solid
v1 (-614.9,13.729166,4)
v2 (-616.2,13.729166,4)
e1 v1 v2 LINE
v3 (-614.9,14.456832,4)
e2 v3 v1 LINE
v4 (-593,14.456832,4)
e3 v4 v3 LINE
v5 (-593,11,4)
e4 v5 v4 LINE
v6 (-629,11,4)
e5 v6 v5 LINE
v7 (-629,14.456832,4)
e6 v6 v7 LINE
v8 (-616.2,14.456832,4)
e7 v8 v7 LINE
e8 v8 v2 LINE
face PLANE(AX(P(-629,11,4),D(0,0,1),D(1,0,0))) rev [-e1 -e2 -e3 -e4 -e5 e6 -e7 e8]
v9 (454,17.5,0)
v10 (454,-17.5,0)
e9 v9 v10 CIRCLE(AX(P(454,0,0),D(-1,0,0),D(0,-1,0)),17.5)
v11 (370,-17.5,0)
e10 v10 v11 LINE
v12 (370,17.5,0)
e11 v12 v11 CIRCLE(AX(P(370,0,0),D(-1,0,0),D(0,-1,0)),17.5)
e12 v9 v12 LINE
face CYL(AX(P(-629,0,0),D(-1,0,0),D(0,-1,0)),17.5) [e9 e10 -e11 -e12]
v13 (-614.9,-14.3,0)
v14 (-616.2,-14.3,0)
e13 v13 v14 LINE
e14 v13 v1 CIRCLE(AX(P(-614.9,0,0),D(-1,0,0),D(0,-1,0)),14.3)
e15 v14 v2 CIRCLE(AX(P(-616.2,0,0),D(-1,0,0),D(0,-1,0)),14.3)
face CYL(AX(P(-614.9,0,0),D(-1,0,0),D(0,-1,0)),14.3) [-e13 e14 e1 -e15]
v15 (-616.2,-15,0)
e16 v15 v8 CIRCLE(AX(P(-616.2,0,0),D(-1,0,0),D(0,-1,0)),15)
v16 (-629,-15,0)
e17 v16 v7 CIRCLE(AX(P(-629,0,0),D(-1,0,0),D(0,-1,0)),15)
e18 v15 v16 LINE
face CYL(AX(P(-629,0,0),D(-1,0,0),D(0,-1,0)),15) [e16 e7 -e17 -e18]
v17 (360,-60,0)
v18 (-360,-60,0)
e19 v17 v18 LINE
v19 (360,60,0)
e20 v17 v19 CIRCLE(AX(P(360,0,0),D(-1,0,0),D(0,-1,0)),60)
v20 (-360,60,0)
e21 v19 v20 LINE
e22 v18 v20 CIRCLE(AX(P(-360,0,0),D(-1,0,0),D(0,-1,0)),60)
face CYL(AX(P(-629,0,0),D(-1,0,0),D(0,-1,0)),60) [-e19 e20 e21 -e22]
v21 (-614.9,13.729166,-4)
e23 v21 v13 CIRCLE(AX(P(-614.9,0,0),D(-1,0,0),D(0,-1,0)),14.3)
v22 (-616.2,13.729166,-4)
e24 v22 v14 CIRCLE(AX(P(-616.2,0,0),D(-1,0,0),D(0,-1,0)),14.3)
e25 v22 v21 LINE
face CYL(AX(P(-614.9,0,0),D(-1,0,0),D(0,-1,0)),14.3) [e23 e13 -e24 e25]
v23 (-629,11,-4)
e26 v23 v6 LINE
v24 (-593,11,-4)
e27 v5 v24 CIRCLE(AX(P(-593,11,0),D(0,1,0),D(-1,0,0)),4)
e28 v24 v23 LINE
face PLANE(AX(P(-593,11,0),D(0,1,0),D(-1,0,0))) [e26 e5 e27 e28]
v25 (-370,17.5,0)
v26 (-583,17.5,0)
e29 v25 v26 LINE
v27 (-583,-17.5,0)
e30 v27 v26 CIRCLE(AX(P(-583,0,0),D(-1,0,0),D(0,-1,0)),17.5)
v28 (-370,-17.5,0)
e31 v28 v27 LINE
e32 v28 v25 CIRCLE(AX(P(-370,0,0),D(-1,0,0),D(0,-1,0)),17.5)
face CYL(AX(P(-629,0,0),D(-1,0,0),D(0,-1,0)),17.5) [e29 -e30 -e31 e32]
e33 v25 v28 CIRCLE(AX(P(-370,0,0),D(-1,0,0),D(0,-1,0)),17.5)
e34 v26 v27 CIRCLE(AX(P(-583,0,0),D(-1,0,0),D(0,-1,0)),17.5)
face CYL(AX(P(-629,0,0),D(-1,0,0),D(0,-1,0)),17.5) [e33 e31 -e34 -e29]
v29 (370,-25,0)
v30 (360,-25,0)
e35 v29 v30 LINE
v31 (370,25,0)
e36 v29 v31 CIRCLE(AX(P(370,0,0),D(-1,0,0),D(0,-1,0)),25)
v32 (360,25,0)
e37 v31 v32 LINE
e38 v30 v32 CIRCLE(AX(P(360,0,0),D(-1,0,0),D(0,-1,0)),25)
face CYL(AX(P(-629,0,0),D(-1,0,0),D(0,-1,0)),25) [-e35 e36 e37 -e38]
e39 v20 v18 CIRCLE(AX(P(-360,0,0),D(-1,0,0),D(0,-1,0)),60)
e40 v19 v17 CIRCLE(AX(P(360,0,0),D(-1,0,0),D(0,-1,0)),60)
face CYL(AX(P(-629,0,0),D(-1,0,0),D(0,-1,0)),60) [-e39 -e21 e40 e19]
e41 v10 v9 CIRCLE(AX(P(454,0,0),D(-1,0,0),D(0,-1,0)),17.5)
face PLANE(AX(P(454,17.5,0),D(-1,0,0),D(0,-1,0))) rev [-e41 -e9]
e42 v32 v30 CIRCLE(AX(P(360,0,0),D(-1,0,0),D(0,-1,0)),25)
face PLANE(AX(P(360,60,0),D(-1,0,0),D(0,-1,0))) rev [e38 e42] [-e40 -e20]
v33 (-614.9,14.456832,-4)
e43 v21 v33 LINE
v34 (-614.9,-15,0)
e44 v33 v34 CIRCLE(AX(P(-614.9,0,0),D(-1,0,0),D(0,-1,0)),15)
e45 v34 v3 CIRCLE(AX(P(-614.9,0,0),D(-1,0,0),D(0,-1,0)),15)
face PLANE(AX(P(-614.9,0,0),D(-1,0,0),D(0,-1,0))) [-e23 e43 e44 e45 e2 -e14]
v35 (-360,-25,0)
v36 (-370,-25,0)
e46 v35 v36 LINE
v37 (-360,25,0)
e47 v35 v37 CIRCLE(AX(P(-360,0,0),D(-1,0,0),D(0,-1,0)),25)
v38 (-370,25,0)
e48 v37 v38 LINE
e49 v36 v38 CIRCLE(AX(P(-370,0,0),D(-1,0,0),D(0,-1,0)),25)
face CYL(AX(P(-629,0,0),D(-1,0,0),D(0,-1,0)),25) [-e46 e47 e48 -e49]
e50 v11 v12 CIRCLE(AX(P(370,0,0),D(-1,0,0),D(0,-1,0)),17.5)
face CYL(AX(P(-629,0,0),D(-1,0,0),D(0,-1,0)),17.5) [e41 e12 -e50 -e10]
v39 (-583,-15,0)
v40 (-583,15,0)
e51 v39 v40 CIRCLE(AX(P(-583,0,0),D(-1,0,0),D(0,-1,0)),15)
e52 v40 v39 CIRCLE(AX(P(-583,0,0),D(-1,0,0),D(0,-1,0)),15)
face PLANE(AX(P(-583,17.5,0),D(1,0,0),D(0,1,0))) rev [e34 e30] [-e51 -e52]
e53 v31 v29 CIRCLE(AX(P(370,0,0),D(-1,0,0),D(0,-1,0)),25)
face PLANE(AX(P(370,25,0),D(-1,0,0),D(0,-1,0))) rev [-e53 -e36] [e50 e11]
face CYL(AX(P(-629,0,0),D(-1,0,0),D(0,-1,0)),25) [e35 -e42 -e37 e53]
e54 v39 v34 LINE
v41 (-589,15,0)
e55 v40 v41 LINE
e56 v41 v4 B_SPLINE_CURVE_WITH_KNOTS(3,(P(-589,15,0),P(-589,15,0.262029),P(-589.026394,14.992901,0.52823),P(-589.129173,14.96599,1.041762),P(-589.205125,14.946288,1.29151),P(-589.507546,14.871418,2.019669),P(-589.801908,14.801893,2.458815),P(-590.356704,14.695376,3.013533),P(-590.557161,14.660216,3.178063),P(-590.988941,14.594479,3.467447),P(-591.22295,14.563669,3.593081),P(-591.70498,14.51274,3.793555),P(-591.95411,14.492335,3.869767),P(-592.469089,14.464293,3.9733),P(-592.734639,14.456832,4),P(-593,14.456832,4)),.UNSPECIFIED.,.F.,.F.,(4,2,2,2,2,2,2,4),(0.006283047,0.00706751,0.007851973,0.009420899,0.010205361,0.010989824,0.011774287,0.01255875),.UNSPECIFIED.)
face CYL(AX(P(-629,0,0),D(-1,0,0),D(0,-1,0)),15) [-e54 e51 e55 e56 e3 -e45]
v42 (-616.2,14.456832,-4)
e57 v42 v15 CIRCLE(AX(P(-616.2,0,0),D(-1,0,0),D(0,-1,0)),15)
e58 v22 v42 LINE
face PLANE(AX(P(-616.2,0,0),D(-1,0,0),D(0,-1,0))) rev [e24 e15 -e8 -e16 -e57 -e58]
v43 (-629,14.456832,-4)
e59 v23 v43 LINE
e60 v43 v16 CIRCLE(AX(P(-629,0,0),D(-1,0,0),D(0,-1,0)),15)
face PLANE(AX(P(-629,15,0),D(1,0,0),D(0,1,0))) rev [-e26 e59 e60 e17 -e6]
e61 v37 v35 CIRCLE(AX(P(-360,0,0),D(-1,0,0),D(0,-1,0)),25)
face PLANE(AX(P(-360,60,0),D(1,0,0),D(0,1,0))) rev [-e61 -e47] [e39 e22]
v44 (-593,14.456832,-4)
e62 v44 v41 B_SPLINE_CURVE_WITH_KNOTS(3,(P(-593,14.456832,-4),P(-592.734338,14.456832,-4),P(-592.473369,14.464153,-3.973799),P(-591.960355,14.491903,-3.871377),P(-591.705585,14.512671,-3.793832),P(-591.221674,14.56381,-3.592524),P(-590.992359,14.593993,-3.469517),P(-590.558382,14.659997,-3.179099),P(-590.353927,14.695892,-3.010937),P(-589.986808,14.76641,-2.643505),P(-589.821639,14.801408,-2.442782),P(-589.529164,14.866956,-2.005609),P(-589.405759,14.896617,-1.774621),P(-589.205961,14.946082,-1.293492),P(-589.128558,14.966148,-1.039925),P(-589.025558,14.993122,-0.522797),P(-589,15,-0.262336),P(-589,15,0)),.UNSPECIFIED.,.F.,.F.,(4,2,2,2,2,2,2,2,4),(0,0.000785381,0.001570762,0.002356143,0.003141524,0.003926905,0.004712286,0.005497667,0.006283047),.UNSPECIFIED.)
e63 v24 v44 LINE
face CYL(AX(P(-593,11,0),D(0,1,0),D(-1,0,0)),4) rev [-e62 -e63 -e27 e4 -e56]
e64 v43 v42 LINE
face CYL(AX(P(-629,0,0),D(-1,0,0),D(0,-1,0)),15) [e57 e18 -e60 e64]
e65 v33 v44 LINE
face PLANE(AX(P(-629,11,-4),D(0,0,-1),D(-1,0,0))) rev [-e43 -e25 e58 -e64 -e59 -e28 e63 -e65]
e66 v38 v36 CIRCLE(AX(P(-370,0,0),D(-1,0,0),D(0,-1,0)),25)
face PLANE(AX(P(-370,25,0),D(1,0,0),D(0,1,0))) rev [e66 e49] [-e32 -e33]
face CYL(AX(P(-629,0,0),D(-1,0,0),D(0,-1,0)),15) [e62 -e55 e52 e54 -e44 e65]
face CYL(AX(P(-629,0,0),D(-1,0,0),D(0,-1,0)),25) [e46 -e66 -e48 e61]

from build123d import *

# Parameters (mm, degrees)
CUT_EXTRUDE_1_DEPTH = 4
CUT_EXTRUDE_START   = 31.9
SKETCH_3_R          = 15
SKETCH_3_R_2        = 14.3
CUT_EXTRUDE_2_DEPTH = 1.3


with BuildPart() as part:
    # 草图1 → 旋转1 (revolve)
    with BuildSketch(Plane.XY, mode=Mode.PRIVATE) as revolve_1_sk:
        Polygon((-360, 60), (360, 60), (360, 25), (370, 25), (370, 17.5), (454, 17.5), (454, 0), (-629, 0), (-629, 15), (-583, 15), (-583, 17.5), (-370, 17.5), (-370, 25), (-360, 25), align=None)
    revolve(revolve_1_sk.sketch.rotate(Axis((-629, 0, 0), (1, 0, 0)), 180), axis=Axis((-629, 0, 0), (1, 0, 0)))

    # 草图2 → 切除-拉伸1 (cut)
    with BuildSketch(Plane(origin=(0, 15, 0), x_dir=(1, 0, 0), z_dir=(0, 1, 0))):
        with BuildLine():
            Line((-629, 4), (-593, 4))
            ThreePointArc((-593, 4), (-589, 0), (-593, -4))
            Line((-593, -4), (-629, -4))
            Line((-629, -4), (-629, 4))
        make_face()
    extrude(amount=-CUT_EXTRUDE_1_DEPTH, mode=Mode.SUBTRACT)

    # 草图3 → 切除-拉伸2 (cut)
    with BuildSketch(Plane.ZY.offset(583).offset(CUT_EXTRUDE_START)):
        with Locations(Location((0, 0, 0), (0, 0, 270))):
            Circle(SKETCH_3_R)
        Circle(SKETCH_3_R_2, mode=Mode.SUBTRACT)
    extrude(amount=CUT_EXTRUDE_2_DEPTH, mode=Mode.SUBTRACT)


solid = part.part
